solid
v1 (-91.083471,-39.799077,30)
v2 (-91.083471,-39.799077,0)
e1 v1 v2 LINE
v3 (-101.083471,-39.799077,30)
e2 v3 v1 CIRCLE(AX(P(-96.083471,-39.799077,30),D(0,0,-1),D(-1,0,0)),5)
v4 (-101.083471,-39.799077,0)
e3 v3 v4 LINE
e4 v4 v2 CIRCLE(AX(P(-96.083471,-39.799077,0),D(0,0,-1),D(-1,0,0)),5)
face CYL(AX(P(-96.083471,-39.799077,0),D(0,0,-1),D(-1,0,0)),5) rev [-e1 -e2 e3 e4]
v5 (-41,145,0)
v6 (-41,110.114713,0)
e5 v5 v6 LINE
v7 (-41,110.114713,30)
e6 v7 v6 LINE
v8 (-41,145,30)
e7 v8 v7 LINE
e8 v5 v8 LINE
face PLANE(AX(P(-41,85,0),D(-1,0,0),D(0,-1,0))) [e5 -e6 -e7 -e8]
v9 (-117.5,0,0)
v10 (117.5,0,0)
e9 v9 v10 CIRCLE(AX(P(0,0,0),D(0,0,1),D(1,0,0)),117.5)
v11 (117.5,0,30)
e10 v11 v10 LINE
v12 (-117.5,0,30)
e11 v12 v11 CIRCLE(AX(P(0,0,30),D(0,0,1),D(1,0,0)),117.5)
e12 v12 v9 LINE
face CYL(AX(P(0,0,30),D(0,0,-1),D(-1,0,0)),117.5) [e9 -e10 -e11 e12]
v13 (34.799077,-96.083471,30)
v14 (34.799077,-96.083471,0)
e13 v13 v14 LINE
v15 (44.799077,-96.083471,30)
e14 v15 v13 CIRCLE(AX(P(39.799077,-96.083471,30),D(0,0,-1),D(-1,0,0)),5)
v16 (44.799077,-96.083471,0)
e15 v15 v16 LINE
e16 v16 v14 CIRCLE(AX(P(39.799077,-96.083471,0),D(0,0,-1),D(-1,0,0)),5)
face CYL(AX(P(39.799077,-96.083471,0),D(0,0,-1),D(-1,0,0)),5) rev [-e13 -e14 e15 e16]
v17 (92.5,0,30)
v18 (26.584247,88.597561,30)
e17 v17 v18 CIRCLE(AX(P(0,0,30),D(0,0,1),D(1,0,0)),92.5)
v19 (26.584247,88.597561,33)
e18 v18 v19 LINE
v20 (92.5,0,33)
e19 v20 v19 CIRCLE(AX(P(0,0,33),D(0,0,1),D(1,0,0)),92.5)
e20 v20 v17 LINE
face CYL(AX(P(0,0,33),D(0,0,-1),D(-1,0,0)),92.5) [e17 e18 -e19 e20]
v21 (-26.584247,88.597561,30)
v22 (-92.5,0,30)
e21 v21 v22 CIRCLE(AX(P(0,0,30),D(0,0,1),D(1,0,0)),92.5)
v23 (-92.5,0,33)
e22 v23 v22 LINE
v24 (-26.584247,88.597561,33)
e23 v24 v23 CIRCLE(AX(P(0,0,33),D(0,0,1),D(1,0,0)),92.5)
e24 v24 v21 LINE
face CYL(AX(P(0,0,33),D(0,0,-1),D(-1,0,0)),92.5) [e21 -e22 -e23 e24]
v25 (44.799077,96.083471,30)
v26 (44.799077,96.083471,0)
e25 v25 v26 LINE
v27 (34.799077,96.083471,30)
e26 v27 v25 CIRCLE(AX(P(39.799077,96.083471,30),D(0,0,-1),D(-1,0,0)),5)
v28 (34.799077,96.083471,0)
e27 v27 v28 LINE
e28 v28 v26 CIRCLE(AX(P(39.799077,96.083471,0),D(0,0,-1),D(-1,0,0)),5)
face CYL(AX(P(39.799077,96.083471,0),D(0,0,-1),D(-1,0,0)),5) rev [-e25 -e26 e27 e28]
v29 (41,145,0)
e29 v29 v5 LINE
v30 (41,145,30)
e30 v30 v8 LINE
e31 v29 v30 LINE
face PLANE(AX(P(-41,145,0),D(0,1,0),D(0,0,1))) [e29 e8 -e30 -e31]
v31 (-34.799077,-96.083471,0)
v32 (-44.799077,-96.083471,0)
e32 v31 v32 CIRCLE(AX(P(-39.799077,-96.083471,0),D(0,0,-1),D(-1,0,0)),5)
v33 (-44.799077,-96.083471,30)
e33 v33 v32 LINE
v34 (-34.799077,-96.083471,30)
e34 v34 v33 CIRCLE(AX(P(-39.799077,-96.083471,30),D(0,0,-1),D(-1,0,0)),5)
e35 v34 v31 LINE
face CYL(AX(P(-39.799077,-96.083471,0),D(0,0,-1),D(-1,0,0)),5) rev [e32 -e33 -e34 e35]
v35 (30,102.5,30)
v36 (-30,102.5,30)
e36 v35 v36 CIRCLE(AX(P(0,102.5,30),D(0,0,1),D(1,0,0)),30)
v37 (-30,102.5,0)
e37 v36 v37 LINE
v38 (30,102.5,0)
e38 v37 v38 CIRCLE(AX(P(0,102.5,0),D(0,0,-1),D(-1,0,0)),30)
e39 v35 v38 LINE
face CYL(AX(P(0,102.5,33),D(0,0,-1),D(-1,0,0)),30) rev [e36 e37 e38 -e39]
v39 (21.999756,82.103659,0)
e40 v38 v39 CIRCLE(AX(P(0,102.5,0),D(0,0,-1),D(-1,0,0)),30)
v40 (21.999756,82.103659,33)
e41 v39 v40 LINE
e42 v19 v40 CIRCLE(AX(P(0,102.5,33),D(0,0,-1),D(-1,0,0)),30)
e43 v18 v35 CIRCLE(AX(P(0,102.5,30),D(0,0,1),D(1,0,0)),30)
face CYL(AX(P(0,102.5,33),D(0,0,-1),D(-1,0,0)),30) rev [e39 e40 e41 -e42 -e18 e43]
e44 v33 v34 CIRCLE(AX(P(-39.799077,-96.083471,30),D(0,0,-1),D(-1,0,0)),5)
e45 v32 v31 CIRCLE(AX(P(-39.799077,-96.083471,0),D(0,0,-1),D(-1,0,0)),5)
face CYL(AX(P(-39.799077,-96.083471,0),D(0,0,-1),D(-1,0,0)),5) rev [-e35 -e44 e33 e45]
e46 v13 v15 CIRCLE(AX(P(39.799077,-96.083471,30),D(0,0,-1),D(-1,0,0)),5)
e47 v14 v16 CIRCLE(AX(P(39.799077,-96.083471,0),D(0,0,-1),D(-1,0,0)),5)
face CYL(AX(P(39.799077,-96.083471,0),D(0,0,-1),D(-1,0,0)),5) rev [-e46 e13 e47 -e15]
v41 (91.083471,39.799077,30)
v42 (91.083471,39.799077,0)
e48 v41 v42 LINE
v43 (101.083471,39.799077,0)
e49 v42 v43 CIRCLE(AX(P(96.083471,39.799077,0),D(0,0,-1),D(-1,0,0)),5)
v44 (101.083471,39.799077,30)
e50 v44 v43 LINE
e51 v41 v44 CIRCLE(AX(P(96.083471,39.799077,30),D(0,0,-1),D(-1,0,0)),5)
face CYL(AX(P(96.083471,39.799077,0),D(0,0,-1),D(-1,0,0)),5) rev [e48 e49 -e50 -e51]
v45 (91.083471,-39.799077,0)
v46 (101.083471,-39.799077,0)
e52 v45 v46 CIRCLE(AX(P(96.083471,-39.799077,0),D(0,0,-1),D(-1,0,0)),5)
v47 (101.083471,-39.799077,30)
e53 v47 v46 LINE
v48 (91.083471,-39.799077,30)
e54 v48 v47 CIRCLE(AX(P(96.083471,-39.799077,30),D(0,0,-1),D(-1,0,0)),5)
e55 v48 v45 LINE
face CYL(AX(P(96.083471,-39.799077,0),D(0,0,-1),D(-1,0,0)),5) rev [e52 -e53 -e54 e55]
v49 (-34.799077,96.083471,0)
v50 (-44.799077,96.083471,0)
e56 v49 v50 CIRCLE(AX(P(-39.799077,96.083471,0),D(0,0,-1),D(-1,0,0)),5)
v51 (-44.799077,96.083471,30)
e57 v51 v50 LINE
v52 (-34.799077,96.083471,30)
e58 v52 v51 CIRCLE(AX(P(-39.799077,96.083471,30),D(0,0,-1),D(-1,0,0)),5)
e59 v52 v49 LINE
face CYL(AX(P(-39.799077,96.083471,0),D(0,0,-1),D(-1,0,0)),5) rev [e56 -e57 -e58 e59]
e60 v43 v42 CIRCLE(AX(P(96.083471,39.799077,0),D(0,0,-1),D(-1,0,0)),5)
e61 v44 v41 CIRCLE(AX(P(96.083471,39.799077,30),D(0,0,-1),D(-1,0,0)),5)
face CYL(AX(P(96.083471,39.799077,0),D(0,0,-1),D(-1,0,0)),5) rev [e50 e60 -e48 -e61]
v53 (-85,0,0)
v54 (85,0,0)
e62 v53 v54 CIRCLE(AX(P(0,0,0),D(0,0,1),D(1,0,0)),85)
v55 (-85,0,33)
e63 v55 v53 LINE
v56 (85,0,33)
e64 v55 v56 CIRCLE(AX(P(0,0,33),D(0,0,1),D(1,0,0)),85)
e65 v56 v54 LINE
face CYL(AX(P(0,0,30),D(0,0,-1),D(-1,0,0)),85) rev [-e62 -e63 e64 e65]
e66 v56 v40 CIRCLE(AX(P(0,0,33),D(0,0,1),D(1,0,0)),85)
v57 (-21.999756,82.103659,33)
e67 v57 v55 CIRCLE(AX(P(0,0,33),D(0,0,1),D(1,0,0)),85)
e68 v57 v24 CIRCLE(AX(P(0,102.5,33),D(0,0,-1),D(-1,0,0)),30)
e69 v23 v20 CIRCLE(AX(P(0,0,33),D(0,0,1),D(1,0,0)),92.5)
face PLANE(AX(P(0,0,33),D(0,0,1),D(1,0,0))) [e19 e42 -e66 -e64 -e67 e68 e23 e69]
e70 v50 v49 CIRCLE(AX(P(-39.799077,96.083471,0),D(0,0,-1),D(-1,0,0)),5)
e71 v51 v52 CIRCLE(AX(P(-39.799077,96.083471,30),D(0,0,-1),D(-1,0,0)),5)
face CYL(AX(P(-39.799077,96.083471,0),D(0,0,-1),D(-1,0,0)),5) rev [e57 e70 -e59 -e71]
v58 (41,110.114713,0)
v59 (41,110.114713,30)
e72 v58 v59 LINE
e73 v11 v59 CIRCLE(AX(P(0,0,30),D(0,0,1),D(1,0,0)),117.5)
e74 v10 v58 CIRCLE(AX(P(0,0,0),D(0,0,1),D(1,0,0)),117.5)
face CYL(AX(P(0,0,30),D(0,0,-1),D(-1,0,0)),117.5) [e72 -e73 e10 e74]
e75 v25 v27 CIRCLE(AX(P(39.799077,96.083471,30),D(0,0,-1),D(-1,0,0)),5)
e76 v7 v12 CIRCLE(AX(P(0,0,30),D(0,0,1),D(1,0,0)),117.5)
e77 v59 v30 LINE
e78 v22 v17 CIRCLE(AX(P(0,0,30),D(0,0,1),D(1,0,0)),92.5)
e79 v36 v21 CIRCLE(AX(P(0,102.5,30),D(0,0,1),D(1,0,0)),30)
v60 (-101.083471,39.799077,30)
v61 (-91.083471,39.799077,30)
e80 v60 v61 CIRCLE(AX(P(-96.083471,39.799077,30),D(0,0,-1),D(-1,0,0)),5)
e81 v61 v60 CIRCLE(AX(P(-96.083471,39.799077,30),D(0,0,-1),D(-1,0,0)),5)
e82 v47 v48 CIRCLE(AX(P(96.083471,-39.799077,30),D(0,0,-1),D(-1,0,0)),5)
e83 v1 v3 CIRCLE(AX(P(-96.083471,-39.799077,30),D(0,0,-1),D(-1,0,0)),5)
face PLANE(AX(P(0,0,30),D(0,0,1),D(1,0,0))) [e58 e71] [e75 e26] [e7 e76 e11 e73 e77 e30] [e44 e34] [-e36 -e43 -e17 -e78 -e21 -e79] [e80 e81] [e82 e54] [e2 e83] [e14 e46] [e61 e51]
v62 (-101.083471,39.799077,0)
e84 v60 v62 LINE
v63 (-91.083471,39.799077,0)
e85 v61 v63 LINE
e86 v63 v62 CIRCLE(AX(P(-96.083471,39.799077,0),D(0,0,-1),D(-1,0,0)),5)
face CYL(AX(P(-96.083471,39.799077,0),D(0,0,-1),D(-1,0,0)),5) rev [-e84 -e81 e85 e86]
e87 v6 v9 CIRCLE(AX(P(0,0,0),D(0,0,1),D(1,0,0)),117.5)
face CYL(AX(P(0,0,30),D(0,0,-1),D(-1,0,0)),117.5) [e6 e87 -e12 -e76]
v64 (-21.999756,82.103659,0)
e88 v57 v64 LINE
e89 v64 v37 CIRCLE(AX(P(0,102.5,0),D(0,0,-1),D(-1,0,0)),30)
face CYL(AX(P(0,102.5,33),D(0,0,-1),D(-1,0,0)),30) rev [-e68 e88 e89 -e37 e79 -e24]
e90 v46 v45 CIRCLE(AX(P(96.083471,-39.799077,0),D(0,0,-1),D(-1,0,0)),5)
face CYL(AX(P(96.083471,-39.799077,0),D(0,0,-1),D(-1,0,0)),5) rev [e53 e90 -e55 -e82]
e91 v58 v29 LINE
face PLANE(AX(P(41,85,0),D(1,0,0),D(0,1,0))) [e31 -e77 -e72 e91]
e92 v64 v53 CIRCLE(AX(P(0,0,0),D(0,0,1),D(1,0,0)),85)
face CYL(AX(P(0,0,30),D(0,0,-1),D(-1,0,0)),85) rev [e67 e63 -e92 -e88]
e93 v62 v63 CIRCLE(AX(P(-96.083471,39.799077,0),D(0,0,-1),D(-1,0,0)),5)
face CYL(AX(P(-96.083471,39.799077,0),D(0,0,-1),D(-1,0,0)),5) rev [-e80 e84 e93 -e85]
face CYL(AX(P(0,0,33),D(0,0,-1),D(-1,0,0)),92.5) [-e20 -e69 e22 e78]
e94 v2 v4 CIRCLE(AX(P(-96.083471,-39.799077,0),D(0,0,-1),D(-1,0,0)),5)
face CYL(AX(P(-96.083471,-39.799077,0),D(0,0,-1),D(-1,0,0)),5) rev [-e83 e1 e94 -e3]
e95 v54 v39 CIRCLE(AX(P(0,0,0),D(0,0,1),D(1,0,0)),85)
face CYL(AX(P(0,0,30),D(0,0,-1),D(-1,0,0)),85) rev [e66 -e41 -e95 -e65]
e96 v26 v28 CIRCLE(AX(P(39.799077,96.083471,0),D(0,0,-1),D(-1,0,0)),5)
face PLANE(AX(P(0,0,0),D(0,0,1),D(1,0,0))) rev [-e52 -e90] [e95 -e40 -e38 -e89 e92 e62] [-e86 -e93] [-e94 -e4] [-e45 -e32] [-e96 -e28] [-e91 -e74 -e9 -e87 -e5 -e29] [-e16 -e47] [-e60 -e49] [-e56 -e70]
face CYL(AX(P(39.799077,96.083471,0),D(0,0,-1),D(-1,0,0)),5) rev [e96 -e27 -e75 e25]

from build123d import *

# Parameters (mm, degrees)
SKETCH_1_R          = 117.5
SKETCH_1_R_2        = 85
EXTRUDE_1_DEPTH     = 30
SKETCH_3_W          = 82
SKETCH_3_H          = 60
EXTRUDE_5_DEPTH     = 30
HOLE_WIZARD_M8_1_D  = 10
SKETCH_9_R          = 92.5
SKETCH_9_R_2        = 85
EXTRUDE_7_DEPTH     = 3
SKETCH_8_R          = 30
CUT_EXTRUDE_1_DEPTH = 190.526383388


with BuildPart() as part:
    # 草图1 → 凸台-拉伸1 (new body)
    with BuildSketch(Plane.XY):
        Circle(SKETCH_1_R)
        Circle(SKETCH_1_R_2, mode=Mode.SUBTRACT)
    extrude(amount=EXTRUDE_1_DEPTH)

    # 草图3 → 凸台-拉伸5 (add, through all)
    with BuildSketch(Plane.XY.offset(30)):
        with Locations((0, 115)):
            Rectangle(SKETCH_3_W, SKETCH_3_H)
    extrude(amount=-EXTRUDE_5_DEPTH)

    # M8 间隙孔1 (through all)
    with Locations(Plane(origin=(0, 0, 0), x_dir=(-1, 0, 0), z_dir=(0, 0, -1))):
        with Locations((-39.799076966, 96.083471381), (39.799076966, 96.083471381), (96.083471381, 39.799076966), (96.083471381, -39.799076966), (39.799076966, -96.083471381), (-39.799076966, -96.083471381), (-96.083471381, -39.799076966), (-96.083471381, 39.799076966)):
            Hole(HOLE_WIZARD_M8_1_D / 2)

    # 草图9 → 凸台-拉伸7 (add)
    with BuildSketch(Plane.XY.offset(30)):
        Circle(SKETCH_9_R)
        Circle(SKETCH_9_R_2, mode=Mode.SUBTRACT)
    extrude(amount=EXTRUDE_7_DEPTH)

    # 草图8 → 切除-拉伸1 (cut, through all)
    with BuildSketch(Plane(origin=(0, 0, 0), x_dir=(-1, 0, 0), z_dir=(0, 0, -1))):
        with Locations((0, 102.5)):
            Circle(SKETCH_8_R)
    extrude(amount=-CUT_EXTRUDE_1_DEPTH, mode=Mode.SUBTRACT)


solid = part.part
